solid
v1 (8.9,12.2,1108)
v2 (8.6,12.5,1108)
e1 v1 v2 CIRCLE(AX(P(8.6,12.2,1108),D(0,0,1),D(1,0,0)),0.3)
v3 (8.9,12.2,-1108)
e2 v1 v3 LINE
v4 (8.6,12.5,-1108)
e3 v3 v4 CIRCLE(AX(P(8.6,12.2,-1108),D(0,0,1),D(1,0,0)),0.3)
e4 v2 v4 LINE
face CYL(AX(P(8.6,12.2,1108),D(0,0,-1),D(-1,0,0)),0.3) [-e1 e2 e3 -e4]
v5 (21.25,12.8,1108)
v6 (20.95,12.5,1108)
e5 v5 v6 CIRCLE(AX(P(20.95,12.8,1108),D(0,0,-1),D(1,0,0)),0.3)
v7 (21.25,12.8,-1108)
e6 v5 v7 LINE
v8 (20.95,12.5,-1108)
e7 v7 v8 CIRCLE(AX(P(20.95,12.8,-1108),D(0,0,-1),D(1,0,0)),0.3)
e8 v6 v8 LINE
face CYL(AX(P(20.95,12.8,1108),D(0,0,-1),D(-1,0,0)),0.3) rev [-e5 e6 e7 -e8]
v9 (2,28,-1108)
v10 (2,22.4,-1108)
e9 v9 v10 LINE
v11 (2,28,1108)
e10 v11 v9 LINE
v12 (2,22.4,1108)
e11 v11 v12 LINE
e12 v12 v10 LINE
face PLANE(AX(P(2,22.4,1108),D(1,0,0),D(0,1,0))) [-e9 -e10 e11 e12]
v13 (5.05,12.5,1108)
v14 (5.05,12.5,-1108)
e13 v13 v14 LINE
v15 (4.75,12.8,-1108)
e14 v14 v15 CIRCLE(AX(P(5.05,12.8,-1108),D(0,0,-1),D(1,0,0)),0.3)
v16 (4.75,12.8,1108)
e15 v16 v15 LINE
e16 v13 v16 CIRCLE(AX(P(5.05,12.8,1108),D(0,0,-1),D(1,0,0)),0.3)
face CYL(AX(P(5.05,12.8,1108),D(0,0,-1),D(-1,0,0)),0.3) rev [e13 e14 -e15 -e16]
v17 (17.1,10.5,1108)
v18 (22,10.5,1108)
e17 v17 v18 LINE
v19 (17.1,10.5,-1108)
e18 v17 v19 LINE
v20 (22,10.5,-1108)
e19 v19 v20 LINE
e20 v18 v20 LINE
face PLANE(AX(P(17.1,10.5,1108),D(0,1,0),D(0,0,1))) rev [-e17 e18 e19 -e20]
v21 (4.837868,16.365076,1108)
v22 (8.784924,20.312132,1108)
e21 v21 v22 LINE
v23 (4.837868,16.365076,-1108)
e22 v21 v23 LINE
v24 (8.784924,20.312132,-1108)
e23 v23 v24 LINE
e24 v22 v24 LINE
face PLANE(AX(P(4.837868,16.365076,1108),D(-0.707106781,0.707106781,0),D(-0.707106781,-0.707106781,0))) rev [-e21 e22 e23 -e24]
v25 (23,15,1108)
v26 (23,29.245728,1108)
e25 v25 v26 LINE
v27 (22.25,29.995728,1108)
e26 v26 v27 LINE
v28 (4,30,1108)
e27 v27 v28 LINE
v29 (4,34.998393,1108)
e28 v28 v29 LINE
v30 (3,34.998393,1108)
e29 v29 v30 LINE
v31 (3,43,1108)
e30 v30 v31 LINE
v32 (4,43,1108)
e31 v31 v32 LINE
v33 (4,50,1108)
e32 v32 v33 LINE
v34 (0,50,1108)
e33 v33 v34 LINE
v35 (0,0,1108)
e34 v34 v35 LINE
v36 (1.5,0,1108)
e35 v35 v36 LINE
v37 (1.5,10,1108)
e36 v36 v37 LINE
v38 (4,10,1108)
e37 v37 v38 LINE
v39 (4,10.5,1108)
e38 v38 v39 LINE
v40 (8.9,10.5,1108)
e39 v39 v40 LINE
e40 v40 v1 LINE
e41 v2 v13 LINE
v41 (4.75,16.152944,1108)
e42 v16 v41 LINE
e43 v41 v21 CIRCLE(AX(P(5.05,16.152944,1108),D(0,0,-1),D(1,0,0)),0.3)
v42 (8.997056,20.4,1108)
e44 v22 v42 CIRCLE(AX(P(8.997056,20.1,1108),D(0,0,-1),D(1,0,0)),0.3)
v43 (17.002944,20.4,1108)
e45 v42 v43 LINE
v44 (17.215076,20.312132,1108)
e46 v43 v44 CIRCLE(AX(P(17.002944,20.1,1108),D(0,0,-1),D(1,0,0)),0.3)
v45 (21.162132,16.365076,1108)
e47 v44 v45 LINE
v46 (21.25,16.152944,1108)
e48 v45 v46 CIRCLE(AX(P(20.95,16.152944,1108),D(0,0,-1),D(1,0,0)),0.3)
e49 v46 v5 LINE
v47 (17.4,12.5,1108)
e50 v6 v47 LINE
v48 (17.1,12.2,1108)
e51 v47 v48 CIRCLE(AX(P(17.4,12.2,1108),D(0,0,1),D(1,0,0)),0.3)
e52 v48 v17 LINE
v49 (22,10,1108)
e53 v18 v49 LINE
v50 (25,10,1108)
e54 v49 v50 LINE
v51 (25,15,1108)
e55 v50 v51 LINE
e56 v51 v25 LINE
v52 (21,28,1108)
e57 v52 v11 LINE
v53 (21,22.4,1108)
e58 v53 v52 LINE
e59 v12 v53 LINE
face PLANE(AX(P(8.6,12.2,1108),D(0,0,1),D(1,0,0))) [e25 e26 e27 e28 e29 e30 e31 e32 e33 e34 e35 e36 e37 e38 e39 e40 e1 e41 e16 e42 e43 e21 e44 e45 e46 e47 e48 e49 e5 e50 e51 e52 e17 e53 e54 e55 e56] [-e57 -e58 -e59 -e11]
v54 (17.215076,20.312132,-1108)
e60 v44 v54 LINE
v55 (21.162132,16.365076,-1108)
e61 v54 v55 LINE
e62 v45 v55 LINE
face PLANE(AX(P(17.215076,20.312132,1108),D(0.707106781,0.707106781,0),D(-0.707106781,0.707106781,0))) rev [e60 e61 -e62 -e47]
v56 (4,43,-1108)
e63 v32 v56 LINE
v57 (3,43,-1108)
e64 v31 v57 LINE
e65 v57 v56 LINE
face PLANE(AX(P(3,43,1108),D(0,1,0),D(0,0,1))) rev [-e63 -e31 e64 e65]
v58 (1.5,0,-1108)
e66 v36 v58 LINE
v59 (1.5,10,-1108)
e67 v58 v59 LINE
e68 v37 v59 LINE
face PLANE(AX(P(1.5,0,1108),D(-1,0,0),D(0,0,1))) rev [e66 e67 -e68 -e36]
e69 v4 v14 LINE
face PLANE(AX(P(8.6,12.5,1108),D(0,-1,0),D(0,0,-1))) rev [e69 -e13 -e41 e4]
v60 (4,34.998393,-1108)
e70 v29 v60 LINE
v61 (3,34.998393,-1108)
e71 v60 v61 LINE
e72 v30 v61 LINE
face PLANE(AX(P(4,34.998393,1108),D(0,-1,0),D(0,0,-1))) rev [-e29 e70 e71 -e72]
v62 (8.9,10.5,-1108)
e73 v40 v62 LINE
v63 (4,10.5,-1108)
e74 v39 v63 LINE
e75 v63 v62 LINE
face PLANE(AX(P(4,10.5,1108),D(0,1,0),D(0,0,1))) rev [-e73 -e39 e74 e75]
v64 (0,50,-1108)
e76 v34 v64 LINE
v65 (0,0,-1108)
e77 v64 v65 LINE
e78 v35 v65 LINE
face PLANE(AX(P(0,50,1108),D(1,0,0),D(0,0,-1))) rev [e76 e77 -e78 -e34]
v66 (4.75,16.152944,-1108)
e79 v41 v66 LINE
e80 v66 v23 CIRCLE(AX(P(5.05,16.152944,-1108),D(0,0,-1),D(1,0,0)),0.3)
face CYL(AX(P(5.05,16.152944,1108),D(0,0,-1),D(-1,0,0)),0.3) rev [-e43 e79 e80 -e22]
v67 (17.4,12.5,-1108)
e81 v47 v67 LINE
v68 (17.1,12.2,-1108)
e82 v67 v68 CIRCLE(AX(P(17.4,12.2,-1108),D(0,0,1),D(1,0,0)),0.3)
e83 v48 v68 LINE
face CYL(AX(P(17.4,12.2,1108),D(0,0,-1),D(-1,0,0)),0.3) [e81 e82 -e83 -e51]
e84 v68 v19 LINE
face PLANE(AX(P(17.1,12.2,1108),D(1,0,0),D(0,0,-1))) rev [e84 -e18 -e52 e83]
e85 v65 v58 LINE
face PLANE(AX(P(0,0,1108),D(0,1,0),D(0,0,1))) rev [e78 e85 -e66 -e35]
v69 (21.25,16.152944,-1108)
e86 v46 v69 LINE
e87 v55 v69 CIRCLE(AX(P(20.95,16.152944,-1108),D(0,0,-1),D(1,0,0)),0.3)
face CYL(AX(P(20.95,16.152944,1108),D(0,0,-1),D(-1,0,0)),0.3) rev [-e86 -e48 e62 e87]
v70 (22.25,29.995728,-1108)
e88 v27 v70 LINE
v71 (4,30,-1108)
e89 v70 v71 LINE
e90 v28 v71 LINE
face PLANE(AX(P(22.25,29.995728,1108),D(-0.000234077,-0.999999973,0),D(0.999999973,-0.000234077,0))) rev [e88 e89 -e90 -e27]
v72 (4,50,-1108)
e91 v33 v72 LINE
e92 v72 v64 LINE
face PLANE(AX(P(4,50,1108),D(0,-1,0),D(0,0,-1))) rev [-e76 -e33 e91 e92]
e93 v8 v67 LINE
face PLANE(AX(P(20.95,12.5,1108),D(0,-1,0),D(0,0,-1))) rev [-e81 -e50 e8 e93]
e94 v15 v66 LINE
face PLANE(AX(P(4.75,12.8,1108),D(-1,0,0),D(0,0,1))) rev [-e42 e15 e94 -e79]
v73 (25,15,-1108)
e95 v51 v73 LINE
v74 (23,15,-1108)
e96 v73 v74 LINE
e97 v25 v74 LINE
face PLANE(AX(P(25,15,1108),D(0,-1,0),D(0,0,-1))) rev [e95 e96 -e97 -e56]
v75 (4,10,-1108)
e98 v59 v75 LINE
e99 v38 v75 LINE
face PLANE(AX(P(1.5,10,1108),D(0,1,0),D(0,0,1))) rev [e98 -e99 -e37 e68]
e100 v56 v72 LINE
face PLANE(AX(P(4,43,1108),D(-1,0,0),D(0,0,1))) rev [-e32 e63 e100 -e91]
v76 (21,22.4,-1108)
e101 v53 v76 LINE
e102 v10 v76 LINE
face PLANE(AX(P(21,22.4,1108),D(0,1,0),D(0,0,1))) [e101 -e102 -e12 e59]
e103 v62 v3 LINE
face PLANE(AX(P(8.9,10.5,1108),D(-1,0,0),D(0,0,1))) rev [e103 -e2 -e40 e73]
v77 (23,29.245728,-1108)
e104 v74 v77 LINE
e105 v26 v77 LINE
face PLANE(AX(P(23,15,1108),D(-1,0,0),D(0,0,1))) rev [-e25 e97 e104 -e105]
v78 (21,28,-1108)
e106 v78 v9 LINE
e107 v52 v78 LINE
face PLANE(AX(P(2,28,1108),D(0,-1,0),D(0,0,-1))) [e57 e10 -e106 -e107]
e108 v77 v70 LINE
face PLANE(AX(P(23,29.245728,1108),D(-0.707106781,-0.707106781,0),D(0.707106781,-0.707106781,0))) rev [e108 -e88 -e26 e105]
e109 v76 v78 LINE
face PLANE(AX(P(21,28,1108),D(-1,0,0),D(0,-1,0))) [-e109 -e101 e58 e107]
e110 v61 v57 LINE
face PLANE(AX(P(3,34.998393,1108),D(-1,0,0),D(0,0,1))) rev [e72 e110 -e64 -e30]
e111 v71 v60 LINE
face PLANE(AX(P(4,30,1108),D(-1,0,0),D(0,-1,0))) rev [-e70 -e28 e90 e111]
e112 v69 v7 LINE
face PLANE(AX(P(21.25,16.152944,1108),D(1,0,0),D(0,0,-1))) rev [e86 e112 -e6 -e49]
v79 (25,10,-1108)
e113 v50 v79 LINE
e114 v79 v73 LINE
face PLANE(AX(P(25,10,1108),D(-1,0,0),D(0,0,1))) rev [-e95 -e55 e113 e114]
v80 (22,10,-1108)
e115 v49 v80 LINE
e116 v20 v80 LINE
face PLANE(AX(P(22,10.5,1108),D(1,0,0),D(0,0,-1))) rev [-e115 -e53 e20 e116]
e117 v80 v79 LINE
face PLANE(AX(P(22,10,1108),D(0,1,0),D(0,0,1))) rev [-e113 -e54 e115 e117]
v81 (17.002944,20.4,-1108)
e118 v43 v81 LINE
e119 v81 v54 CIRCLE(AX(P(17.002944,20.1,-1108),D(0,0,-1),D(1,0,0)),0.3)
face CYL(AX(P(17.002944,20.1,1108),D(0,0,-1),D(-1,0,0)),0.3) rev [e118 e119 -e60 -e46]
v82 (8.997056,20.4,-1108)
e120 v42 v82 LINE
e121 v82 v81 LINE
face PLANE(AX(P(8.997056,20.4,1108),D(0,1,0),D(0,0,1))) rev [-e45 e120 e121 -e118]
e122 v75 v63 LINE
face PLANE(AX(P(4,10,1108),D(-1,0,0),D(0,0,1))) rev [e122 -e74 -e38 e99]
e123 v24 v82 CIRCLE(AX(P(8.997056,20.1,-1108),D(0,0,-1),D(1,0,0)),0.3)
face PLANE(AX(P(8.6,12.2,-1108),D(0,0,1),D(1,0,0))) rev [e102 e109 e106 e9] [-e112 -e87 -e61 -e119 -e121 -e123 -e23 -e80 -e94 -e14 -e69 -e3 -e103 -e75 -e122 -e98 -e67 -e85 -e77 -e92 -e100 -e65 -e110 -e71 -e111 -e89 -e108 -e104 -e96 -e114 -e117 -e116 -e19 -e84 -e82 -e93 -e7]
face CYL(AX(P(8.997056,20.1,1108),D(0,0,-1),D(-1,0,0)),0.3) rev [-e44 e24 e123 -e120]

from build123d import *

# Parameters (mm, degrees)
SKETCH_2_W      = 19
SKETCH_2_H      = 5.6
EXTRUDE_1_DEPTH = 1108


with BuildPart() as part:
    # 草图2 → 凸台-拉伸1 (new, symmetric)
    with BuildSketch(Plane.XY):
        with BuildLine():
            Line((1.5, 10), (4, 10))
            Line((4, 10), (4, 10.5))
            Line((4, 10.5), (8.9, 10.5))
            Line((8.9, 10.5), (8.9, 12.2))
            ThreePointArc((8.9, 12.2), (8.812132034, 12.412132034), (8.6, 12.5))
            Line((8.6, 12.5), (5.05, 12.5))
            ThreePointArc((5.05, 12.5), (4.837867966, 12.587867966), (4.75, 12.8))
            Line((4.75, 12.8), (4.75, 16.152943725))
            ThreePointArc((4.75, 16.152943725), (4.77283614, 16.267748755), (4.837867966, 16.36507576))
            Line((4.837867966, 16.36507576), (8.78492424, 20.312132034))
            ThreePointArc((8.78492424, 20.312132034), (8.882251245, 20.37716386), (8.997056275, 20.4))
            Line((8.997056275, 20.4), (17.002943725, 20.4))
            ThreePointArc((17.002943725, 20.4), (17.117748755, 20.37716386), (17.21507576, 20.312132034))
            Line((17.21507576, 20.312132034), (21.162132034, 16.36507576))
            ThreePointArc((21.162132034, 16.36507576), (21.22716386, 16.267748755), (21.25, 16.152943725))
            Line((21.25, 16.152943725), (21.25, 12.8))
            ThreePointArc((21.25, 12.8), (21.162132034, 12.587867966), (20.95, 12.5))
            Line((20.95, 12.5), (17.4, 12.5))
            ThreePointArc((17.4, 12.5), (17.187867966, 12.412132034), (17.1, 12.2))
            Line((17.1, 12.2), (17.1, 10.5))
            Line((17.1, 10.5), (22, 10.5))
            Line((22, 10.5), (22, 10))
            Line((22, 10), (25, 10))
            Line((25, 10), (25, 15))
            Line((25, 15), (23, 15))
            Line((23, 15), (23, 29.24572809))
            Line((23, 29.24572809), (22.25, 29.99572809))
            Line((22.25, 29.99572809), (4, 30))
            Line((4, 30), (4, 34.998393128))
            Line((4, 34.998393128), (3, 34.998393128))
            Line((3, 34.998393128), (3, 43))
            Line((3, 43), (4, 43))
            Line((4, 43), (4, 50))
            Line((4, 50), (0, 50))
            Line((0, 50), (0, 0))
            Line((0, 0), (1.5, 0))
            Line((1.5, 0), (1.5, 10))
        make_face()
        with Locations((11.5, 25.2)):
            Rectangle(SKETCH_2_W, SKETCH_2_H, mode=Mode.SUBTRACT)
    extrude(amount=EXTRUDE_1_DEPTH, both=True)


solid = part.part
